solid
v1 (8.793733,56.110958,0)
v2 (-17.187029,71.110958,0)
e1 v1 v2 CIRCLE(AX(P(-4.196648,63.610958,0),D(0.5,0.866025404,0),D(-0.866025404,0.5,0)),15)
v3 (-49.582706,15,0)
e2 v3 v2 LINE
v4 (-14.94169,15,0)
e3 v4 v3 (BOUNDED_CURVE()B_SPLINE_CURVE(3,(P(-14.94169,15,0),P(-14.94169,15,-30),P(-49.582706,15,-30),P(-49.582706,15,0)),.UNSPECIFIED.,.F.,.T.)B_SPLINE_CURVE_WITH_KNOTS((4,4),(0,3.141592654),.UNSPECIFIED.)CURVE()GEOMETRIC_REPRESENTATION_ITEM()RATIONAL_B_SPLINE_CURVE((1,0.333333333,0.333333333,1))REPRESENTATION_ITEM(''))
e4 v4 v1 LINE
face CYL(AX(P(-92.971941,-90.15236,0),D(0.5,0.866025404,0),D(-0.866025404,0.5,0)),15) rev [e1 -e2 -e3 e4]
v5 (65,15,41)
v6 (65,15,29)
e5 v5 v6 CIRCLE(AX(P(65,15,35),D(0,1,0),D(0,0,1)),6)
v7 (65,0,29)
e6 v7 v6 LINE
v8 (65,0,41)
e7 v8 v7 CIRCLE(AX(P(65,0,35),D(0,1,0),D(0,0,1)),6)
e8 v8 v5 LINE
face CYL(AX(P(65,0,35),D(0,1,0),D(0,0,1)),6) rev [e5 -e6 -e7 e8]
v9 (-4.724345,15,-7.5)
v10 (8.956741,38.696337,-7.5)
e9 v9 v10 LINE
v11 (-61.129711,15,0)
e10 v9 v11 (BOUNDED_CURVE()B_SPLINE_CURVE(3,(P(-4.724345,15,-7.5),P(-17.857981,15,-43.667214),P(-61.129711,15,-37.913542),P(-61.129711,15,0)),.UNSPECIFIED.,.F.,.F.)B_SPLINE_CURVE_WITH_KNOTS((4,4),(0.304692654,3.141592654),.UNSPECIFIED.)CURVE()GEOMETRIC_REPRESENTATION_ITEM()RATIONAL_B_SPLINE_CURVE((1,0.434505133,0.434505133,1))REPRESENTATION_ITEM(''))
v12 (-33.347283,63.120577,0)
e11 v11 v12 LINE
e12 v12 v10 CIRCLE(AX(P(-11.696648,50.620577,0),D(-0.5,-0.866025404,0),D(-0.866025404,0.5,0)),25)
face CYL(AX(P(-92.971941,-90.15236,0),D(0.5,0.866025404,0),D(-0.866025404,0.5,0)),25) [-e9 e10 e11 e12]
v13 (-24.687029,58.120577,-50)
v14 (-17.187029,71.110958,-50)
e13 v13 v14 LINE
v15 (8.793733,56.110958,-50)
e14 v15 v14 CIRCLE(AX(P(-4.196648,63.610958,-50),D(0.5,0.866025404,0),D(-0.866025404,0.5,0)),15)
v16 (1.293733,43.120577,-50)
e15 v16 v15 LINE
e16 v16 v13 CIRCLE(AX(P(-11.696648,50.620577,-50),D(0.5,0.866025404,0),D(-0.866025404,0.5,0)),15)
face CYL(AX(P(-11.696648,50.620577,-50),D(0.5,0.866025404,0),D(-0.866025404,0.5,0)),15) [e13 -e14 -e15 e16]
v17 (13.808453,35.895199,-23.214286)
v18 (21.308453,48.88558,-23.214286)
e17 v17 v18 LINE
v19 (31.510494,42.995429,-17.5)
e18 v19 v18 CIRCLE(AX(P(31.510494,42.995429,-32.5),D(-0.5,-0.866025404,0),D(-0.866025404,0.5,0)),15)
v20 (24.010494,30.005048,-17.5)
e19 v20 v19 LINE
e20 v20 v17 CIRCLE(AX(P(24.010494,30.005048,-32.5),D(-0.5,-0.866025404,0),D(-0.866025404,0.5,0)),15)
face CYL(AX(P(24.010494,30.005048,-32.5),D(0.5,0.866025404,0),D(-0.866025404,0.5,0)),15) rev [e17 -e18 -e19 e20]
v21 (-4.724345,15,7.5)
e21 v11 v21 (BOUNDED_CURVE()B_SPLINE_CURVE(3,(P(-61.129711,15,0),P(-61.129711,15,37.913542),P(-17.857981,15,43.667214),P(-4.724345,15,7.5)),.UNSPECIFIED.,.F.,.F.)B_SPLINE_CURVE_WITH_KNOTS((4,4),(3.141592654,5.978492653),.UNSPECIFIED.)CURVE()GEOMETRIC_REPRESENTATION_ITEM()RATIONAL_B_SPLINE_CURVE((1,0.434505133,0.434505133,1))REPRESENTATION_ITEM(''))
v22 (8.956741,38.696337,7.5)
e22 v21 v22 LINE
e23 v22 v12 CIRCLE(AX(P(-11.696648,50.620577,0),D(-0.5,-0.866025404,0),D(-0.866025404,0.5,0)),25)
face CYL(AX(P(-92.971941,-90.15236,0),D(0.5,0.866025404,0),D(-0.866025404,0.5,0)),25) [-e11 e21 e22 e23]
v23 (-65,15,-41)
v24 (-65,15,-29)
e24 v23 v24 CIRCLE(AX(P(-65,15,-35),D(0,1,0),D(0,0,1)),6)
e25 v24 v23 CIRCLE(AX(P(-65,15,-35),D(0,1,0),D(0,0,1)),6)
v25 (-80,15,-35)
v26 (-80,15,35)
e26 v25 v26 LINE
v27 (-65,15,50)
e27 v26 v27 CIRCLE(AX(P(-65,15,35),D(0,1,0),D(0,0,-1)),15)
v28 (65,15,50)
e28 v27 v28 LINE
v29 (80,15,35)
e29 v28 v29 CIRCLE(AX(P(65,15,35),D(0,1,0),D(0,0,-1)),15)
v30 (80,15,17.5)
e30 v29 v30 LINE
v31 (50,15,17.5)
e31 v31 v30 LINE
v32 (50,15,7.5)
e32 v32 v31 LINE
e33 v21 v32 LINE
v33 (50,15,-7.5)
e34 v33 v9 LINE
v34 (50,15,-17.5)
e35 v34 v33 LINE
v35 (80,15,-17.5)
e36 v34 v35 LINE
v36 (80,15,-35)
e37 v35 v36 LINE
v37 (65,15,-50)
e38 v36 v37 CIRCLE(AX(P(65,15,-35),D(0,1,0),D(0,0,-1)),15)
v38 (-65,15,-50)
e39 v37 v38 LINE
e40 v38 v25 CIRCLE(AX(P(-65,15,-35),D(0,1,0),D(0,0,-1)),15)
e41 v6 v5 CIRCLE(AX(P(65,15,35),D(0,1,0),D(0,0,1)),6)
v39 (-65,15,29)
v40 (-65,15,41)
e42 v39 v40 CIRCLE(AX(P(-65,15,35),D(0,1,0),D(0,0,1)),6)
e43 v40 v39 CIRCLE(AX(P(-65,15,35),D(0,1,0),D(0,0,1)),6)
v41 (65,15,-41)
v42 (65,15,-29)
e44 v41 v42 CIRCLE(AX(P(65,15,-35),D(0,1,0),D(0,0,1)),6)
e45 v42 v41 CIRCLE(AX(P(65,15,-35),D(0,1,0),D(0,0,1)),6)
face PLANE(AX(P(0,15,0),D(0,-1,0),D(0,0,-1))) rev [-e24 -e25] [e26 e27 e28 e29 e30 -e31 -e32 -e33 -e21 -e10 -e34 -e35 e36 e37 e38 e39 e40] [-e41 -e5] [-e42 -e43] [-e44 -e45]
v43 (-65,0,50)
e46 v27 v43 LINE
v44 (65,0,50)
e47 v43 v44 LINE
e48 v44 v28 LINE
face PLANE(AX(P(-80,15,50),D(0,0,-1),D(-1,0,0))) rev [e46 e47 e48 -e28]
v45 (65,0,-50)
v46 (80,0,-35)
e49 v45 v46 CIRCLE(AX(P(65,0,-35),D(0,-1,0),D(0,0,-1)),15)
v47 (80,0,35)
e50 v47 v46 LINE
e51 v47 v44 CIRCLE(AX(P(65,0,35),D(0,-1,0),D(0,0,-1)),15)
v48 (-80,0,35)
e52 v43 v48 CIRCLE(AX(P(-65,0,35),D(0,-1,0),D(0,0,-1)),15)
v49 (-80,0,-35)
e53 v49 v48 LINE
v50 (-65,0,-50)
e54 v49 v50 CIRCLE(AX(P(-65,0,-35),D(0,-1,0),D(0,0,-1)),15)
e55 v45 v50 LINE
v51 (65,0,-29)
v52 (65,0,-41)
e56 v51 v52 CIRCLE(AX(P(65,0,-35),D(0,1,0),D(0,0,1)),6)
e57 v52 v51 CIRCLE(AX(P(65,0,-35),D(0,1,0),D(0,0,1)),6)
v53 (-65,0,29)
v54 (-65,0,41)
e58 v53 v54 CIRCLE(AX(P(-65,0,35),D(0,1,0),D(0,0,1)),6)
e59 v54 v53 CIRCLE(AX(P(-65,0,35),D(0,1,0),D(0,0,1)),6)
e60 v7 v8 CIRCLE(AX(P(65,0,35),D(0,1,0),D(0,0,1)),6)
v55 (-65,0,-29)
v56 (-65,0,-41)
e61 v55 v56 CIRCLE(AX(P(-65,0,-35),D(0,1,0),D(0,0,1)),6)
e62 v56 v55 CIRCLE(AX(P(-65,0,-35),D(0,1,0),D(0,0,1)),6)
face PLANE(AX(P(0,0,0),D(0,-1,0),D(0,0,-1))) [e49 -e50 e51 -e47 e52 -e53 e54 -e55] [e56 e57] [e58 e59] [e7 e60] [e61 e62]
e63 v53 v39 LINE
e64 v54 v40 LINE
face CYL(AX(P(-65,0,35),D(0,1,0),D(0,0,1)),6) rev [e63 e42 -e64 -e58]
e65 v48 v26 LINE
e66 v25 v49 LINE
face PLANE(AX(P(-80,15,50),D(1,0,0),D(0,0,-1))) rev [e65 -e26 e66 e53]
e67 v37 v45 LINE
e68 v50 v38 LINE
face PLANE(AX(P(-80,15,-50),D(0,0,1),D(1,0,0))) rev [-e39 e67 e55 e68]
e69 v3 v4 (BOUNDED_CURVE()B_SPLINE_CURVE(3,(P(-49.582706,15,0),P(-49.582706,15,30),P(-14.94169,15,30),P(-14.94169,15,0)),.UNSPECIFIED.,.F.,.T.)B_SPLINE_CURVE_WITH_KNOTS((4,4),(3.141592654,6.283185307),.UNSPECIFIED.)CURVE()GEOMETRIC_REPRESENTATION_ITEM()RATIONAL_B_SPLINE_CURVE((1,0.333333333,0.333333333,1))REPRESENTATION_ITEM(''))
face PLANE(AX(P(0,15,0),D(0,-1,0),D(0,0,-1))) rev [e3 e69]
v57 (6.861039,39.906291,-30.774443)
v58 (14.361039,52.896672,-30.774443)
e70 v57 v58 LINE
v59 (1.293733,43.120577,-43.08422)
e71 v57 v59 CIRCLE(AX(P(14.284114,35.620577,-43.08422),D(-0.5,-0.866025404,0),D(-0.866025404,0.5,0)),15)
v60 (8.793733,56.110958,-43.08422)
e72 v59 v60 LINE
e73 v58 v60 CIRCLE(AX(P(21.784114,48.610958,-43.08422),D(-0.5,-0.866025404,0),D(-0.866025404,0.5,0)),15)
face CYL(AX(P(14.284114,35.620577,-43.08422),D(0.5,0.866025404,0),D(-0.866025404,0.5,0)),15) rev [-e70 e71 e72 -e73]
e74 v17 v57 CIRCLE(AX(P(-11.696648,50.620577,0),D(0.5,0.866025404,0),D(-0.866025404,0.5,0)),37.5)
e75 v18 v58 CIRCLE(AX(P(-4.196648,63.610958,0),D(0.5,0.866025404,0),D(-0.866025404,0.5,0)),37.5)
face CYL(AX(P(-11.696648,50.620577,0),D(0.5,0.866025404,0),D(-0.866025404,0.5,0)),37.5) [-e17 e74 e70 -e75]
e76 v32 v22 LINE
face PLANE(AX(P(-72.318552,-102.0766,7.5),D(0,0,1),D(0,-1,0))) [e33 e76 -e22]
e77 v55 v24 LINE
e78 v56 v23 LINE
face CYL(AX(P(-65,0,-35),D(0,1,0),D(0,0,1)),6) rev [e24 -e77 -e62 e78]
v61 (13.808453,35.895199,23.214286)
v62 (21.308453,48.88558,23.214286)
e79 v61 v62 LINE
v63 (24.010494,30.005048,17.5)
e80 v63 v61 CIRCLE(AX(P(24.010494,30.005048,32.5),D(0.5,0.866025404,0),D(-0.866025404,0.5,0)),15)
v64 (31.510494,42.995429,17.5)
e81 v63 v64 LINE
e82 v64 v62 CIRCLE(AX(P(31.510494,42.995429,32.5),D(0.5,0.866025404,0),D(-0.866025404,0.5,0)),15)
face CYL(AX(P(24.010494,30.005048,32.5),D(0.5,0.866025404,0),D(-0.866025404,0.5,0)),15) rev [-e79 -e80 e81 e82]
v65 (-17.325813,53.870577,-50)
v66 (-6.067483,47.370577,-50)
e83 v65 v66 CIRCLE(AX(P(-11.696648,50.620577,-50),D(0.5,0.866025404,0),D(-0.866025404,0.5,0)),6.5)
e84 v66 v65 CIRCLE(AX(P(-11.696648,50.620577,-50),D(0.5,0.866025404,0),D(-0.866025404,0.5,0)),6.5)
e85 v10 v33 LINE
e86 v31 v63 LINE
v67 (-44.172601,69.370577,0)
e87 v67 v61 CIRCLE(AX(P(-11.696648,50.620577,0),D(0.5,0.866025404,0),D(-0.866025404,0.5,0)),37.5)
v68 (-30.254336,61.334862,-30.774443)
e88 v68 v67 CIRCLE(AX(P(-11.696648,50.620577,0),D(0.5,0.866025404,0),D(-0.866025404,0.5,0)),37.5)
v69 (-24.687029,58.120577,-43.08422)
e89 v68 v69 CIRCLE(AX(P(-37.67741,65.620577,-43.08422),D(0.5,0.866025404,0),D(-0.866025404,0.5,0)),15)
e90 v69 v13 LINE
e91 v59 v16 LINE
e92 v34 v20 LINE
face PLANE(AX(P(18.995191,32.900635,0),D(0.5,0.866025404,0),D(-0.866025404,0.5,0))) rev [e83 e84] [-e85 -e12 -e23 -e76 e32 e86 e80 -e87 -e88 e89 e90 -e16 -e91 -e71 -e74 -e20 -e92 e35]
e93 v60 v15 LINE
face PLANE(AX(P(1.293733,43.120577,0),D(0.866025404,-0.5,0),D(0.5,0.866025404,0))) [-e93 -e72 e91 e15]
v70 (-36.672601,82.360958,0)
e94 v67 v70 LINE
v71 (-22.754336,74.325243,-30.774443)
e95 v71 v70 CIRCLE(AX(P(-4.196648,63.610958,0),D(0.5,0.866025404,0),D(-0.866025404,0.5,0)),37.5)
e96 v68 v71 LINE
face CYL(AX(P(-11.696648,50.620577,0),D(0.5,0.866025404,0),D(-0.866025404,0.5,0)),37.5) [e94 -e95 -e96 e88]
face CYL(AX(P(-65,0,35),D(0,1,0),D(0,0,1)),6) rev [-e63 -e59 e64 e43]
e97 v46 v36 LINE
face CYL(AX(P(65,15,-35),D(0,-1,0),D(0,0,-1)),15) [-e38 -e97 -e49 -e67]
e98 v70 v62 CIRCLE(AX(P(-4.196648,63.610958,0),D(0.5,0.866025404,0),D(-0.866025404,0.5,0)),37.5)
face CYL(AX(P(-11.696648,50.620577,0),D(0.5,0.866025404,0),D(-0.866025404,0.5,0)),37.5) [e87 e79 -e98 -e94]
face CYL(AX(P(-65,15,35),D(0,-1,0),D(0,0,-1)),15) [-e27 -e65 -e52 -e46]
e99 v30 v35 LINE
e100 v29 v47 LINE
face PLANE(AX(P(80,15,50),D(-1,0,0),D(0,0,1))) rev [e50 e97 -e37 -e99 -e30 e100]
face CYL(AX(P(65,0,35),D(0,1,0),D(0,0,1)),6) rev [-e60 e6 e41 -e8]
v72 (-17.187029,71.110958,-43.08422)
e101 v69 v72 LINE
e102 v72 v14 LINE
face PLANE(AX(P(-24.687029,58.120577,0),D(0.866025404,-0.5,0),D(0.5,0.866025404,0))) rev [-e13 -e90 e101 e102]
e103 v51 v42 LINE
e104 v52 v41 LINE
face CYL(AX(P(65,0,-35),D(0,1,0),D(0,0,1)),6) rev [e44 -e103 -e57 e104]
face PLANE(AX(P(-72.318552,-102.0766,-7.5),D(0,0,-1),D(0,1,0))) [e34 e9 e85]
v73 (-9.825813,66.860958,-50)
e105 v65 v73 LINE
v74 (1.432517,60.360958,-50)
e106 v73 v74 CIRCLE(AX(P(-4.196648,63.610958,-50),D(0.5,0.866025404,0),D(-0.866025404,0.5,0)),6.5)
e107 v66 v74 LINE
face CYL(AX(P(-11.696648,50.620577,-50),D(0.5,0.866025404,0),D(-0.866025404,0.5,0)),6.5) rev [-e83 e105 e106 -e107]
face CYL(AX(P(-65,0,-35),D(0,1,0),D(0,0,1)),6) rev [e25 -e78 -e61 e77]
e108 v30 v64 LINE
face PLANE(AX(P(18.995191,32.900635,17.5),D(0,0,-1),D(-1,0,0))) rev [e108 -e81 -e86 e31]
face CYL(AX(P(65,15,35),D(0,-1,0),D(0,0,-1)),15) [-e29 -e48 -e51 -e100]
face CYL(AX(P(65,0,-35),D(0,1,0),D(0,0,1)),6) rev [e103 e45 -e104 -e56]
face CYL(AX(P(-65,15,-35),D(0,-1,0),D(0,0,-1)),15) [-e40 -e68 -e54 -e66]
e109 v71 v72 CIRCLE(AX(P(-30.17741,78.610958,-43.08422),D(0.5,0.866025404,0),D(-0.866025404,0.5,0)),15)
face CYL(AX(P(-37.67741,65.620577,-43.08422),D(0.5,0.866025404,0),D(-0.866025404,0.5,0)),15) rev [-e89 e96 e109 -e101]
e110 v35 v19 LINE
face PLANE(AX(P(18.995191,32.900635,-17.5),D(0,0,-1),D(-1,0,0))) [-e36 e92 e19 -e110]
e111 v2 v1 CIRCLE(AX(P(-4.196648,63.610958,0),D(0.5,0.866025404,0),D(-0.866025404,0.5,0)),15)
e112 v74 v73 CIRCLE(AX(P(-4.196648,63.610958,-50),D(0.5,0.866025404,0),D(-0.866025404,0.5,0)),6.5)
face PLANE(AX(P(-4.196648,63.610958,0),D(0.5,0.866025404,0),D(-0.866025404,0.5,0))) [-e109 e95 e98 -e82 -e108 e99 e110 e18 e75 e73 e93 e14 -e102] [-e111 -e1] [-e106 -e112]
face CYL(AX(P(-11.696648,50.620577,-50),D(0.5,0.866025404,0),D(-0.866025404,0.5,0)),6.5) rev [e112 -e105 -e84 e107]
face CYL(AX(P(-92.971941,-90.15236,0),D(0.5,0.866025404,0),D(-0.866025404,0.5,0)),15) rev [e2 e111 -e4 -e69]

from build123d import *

# Parameters (mm, degrees)
BASE_PLATE_SKETCH_W             = 160
BASE_PLATE_SKETCH_H             = 100
BASE_PLATE_160X100X15_DEPTH     = 15
BASE_PLATE_CORNER_FILLETS_R15_R = 15
MOUNTING_HOLES_SKETCH_R         = 6
MOUNTING_HOLES_4X_12_DEPTH      = 15
INCLINED_ARM_PROFILE_SKETCH_R   = 15
INCLINED_ARM_PROFILE_SKETCH_R_2 = 6.5
INCLINED_ARM_DEPTH              = 15
ARM_SUPPORT_WEB_REACH           = 134.937
ARM_SUPPORT_WEB_SKETCH_R        = 15


with BuildPart() as part:
    # Base Plate Sketch → Base Plate 160x100x15 (new body)
    with BuildSketch(Plane(origin=(0, 0, 0), x_dir=(1, 0, 0), z_dir=(0, 1, 0))):
        Rectangle(BASE_PLATE_SKETCH_W, BASE_PLATE_SKETCH_H)
    extrude(amount=BASE_PLATE_160X100X15_DEPTH)

    # Base Plate Corner Fillets R15
    base_plate_corner_fillets_r15_edges = [part.edges().sort_by_distance(p)[0] for p in [
        (80, 7.5, 50),
        (-80, 7.5, 50),
        (-80, 7.5, -50),
        (80, 7.5, -50),
    ]]
    fillet(base_plate_corner_fillets_r15_edges, radius=BASE_PLATE_CORNER_FILLETS_R15_R)

    # Mounting Holes Sketch → Mounting Holes 4x_12 (cut)
    with BuildSketch(Plane(origin=(0, 15, 0), x_dir=(1, 0, 0), z_dir=(0, 1, 0))):
        with Locations(Location((-65, 35, 0), (0, 0, 270))):
            Circle(MOUNTING_HOLES_SKETCH_R)
        with Locations(Location((65, 35, 0), (0, 0, 270))):
            Circle(MOUNTING_HOLES_SKETCH_R)
        with Locations(Location((65, -35, 0), (0, 0, 270))):
            Circle(MOUNTING_HOLES_SKETCH_R)
        with Locations(Location((-65, -35, 0), (0, 0, 270))):
            Circle(MOUNTING_HOLES_SKETCH_R)
    extrude(amount=-MOUNTING_HOLES_4X_12_DEPTH, mode=Mode.SUBTRACT)

    # Arm Support Web: up to this face of the body (flat: up to its plane)
    arm_support_web_end = Plane(part.part.faces().sort_by_distance((0, 15, 0))[0])
    # Arm Support Web Sketch → Arm Support Web (add, up to the picked face)
    with BuildSketch(Plane(origin=(26.495190528, 45.891016151, 0), x_dir=(0.8660254037844417, -0.4999999999999947, 0), z_dir=(0.4999999999999947, 0.8660254037844417, 0)), mode=Mode.PRIVATE) as arm_support_web_sk1:
        with BuildLine():
            Line((61.782032303, 7.5), (61.782032303, -7.5))
            Line((61.782032303, -7.5), (-11.591402841, -7.5))
            ThreePointArc((-11.591402841, -7.5), (-60.439882876, 0), (-11.591402841, 7.5))
            Line((-11.591402841, 7.5), (61.782032303, 7.5))
        make_face()
        with Locations(Location((-35.439882876, 0, 0), (0, 0, 180))):
            Circle(ARM_SUPPORT_WEB_SKETCH_R, mode=Mode.SUBTRACT)
    arm_support_web_tool1 = split(extrude(arm_support_web_sk1.sketch, amount=-ARM_SUPPORT_WEB_REACH, mode=Mode.PRIVATE), bisect_by=arm_support_web_end, keep=Keep.BOTH, mode=Mode.PRIVATE)


with BuildPart() as body_2:
    # Inclined Arm Profile Sketch → Inclined Arm (new body)
    with BuildSketch(Plane(origin=(26.495190528, 45.891016151, 0), x_dir=(-0.8660254037844417, 0.4999999999999947, 0), z_dir=(0.4999999999999947, 0.8660254037844417, 0))):
        with BuildLine():
            Line((-61.782032303, -17.5), (-5.79117338, -17.5))
            ThreePointArc((-5.79117338, -17.5), (0.755363327, -19.003968837), (5.989128407, -23.214285714))
            ThreePointArc((5.989128407, -23.214285714), (9.720912357, -27.290741204), (14.011311447, -30.774442749))
            ThreePointArc((14.011311447, -30.774442749), (18.735961782, -36.140569101), (20.439882876, -43.084219849))
            Line((20.439882876, -43.084219849), (20.439882876, -50))
            ThreePointArc((20.439882876, -50), (35.439882876, -65), (50.439882876, -50))
            Line((50.439882876, -50), (50.439882876, -43.084219849))
            ThreePointArc((50.439882876, -43.084219849), (52.14380397, -36.140569101), (56.868454305, -30.774442749))
            ThreePointArc((56.868454305, -30.774442749), (62.73062408, 25.718970519), (5.989128407, 23.214285714))
            ThreePointArc((5.989128407, 23.214285714), (0.755363327, 19.003968837), (-5.79117338, 17.5))
            Line((-5.79117338, 17.5), (-61.782032303, 17.5))
            Line((-61.782032303, 17.5), (-61.782032303, -17.5))
        make_face()
        with Locations((35.439882876, 0)):
            Circle(INCLINED_ARM_PROFILE_SKETCH_R, mode=Mode.SUBTRACT)
        with Locations((35.439882876, -50)):
            Circle(INCLINED_ARM_PROFILE_SKETCH_R_2, mode=Mode.SUBTRACT)
    extrude(amount=-INCLINED_ARM_DEPTH)


with BuildPart() as part_1:
    add(part.part)

    add(body_2.part)  # Arm Support Web merges body 2
    add(arm_support_web_tool1.solids().sort_by(Axis((20.297634, 49.469177, 0), (-0.4999999999999947, -0.8660254037844417, 0)))[0])


solid = part_1.part
